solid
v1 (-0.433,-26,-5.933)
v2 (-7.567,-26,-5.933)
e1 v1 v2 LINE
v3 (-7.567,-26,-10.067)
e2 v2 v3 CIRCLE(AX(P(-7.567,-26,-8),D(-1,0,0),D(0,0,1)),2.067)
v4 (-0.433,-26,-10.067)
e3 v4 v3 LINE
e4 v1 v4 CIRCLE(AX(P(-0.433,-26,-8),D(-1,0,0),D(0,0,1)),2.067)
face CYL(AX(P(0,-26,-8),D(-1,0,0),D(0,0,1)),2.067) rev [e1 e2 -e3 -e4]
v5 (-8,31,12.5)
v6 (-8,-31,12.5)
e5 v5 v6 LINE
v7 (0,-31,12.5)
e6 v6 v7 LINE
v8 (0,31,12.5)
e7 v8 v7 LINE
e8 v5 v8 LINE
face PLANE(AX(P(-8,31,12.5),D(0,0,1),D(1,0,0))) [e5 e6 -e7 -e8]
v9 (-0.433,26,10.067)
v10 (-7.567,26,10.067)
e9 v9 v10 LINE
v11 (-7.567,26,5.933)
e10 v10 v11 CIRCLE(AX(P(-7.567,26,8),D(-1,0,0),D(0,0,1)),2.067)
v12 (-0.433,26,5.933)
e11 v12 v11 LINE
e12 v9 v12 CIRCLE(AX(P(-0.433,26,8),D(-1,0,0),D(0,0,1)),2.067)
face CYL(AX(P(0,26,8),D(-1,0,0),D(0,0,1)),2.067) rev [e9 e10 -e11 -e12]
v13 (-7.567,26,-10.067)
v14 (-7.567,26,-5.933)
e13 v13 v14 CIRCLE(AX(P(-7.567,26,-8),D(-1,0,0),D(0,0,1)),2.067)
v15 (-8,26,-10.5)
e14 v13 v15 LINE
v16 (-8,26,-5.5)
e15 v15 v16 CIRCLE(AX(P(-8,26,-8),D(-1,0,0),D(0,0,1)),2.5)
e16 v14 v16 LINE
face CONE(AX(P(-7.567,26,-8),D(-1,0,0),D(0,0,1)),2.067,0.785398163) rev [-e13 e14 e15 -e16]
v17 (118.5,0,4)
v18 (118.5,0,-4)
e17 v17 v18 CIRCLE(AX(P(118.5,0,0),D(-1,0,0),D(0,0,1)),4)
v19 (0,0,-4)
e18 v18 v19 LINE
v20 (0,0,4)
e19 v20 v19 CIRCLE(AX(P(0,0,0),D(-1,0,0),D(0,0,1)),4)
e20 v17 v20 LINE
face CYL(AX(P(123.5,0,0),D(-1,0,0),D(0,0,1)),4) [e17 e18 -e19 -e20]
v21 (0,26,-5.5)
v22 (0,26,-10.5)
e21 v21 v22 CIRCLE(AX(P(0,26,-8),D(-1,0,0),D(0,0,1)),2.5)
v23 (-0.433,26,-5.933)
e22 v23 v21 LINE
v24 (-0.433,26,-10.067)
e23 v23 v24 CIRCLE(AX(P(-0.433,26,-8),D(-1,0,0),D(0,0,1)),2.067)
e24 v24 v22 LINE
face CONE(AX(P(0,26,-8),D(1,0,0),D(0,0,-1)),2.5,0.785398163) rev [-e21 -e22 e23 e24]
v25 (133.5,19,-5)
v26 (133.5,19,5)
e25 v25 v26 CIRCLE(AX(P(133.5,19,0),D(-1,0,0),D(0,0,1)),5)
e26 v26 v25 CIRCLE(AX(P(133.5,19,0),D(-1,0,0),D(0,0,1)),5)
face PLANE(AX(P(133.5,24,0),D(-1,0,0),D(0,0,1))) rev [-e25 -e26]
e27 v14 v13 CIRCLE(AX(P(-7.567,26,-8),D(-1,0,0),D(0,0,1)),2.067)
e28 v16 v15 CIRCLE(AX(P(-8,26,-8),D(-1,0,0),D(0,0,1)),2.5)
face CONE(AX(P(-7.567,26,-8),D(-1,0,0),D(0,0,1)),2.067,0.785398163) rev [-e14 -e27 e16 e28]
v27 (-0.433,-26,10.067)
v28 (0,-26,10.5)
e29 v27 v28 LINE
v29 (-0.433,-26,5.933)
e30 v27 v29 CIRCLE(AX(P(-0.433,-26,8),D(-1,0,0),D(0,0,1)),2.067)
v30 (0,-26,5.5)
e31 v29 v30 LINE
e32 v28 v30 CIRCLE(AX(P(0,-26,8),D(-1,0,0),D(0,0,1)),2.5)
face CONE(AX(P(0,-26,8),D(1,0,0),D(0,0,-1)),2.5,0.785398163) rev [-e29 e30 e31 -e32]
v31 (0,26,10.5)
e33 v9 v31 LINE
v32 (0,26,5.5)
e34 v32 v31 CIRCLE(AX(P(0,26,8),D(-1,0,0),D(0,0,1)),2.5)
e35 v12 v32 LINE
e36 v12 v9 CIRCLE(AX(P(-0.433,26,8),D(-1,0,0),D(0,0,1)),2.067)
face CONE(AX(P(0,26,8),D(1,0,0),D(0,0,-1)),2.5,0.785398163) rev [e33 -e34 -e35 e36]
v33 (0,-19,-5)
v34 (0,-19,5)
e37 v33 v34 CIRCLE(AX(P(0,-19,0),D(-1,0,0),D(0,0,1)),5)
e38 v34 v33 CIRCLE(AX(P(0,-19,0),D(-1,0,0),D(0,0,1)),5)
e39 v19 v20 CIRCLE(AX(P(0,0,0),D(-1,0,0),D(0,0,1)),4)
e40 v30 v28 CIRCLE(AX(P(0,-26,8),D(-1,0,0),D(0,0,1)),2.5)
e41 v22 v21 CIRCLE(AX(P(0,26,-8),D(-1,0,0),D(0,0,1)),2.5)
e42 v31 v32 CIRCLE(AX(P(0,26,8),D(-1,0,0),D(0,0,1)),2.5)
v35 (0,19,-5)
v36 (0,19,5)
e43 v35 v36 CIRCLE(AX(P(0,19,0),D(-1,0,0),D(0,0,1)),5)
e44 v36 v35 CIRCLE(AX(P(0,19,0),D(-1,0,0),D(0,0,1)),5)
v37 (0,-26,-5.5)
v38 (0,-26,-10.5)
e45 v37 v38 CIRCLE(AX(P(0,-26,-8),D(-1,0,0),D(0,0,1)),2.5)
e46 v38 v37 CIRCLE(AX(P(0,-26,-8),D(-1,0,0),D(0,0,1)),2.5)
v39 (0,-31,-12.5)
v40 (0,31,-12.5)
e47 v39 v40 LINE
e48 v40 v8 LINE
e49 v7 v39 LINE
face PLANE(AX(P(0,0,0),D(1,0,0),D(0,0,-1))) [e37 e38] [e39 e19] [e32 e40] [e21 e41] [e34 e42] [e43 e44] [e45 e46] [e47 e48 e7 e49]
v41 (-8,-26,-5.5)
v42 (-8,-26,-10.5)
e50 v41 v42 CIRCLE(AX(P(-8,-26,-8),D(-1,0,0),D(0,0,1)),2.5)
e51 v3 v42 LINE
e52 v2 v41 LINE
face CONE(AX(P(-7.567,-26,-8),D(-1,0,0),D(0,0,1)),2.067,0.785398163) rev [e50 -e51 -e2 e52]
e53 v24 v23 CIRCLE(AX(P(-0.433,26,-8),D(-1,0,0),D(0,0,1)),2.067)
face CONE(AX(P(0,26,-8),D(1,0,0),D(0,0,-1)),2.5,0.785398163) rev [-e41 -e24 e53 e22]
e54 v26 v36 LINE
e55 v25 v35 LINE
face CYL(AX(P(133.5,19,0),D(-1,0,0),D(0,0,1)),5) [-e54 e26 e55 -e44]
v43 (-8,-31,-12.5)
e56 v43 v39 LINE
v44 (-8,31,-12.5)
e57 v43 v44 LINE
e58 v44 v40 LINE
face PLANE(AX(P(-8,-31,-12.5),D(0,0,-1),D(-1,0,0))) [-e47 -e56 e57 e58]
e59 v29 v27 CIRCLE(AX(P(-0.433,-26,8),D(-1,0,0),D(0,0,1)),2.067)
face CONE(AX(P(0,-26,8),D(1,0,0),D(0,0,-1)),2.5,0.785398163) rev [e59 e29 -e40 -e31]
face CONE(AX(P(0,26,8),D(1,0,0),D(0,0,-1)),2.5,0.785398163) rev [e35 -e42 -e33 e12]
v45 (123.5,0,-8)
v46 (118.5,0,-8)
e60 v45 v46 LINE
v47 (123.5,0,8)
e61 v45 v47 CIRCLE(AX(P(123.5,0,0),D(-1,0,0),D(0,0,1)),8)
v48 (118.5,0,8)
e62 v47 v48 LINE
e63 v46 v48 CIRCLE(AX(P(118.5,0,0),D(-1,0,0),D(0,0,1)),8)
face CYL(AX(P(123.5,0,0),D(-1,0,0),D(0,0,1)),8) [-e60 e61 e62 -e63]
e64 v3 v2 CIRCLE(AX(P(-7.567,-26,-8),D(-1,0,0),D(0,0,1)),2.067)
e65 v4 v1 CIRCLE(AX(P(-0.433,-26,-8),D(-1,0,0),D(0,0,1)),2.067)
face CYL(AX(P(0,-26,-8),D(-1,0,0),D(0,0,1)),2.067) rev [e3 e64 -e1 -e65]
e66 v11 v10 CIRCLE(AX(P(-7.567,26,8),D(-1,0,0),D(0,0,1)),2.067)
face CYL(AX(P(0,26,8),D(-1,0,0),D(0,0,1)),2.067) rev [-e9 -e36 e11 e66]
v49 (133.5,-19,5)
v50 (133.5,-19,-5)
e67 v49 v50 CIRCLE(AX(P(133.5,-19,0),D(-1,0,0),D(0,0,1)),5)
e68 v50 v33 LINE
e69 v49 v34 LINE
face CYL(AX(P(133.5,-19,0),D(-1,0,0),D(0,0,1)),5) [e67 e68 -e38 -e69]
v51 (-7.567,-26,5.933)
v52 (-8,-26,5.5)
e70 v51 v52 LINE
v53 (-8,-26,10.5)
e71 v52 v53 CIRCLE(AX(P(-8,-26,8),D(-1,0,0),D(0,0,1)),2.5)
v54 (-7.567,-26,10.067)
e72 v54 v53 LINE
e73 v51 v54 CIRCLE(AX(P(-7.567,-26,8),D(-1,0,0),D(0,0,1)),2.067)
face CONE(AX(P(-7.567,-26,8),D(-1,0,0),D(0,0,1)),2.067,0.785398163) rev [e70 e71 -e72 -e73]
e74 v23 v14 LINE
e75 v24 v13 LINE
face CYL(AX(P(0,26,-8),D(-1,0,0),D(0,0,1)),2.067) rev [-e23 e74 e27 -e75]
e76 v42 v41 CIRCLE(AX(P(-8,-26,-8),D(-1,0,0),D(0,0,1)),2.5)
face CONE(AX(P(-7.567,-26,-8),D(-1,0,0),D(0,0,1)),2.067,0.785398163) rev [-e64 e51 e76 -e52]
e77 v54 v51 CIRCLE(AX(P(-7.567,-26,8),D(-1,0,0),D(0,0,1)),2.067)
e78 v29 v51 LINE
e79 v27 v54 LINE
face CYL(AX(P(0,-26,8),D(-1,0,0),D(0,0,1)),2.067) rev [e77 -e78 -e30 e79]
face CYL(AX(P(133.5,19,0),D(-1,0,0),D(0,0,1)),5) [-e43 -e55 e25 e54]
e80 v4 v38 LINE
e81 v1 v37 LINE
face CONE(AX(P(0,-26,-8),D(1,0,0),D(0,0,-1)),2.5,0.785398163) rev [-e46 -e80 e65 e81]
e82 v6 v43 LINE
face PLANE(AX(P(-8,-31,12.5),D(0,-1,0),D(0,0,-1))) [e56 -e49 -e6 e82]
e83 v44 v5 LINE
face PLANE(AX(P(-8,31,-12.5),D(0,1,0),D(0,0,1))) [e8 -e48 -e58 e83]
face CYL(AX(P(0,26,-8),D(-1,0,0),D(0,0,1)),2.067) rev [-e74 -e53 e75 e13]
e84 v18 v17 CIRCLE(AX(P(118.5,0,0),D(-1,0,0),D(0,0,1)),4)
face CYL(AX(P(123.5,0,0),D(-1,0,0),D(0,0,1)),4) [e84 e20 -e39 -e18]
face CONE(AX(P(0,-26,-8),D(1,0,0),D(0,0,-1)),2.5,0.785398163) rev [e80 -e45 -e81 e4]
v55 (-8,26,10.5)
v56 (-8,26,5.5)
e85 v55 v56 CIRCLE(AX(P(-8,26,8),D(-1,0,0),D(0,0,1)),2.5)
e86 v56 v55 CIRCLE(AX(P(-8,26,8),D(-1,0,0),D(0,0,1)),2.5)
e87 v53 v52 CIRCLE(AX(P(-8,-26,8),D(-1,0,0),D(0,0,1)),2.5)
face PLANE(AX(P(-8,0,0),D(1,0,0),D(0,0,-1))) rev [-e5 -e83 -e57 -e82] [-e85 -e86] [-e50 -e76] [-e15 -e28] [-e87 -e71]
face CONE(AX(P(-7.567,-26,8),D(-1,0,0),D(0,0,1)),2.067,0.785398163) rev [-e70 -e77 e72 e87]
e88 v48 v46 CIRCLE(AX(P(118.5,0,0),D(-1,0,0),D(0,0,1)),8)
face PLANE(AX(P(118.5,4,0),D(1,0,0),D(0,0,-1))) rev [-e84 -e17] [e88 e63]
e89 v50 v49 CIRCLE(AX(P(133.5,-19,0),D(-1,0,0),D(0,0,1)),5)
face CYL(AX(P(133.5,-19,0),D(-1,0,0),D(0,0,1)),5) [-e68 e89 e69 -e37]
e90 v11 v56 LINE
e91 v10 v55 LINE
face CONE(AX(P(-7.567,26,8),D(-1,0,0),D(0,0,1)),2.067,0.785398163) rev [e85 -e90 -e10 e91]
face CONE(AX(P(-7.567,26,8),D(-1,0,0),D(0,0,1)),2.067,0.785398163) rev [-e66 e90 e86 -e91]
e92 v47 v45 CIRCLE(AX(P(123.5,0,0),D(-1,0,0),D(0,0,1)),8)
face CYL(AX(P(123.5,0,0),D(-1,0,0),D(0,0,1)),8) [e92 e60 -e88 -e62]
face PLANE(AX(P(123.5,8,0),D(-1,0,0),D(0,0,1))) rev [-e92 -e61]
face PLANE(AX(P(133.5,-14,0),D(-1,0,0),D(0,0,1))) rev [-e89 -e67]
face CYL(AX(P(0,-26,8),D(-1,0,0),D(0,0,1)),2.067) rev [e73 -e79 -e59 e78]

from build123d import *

# Parameters (mm, degrees)
SKETCH_1_W                  = 25
SKETCH_1_H                  = 62
EXTRUDE_1_DEPTH             = 8
SKETCH_2_W                  = 133.5
SKETCH_2_H                  = 5
PATTERN_LINEAR_1_COUNT      = 2
PATTERN_LINEAR_1_PITCH      = 38
PATTERN_LINEAR_2_COUNT      = 2
PATTERN_LINEAR_2_PITCH      = 16
PATTERN_LINEAR_2_COUNT_DIR2 = 2
PATTERN_LINEAR_2_PITCH_DIR2 = 52


with BuildPart() as part:
    # 草图1 → 凸台-拉伸1 (new body)
    with BuildSketch(Plane(origin=(0, 0, 0), x_dir=(0, 0, -1), z_dir=(1, 0, 0))):
        Rectangle(SKETCH_1_W, SKETCH_1_H)
    extrude(amount=-EXTRUDE_1_DEPTH)

    # 草图2 → 旋转1 (revolve)
    with BuildSketch(Plane.XY, mode=Mode.PRIVATE) as revolve_1_sk:
        with Locations((66.75, 21.5)):
            Rectangle(SKETCH_2_W, SKETCH_2_H)
    revolve_1 = revolve(revolve_1_sk.sketch.rotate(Axis((133.5, 19, 0), (-1, 0, 0)), 270), axis=Axis((133.5, 19, 0), (-1, 0, 0)))

    # 阵列(线性)1: 旋转1 ×2
    with Locations(*[(0, -i * PATTERN_LINEAR_1_PITCH, 0) for i in range(1, PATTERN_LINEAR_1_COUNT)]):
        add(revolve_1)

    # 草图4 → 切除-旋转1 (revolve, cut)
    with BuildSketch(Plane.XY.offset(8), mode=Mode.PRIVATE) as cut_revolve_1_sk:
        Polygon((-8, 26), (-8, 28.5), (-7.567, 28.067), (-0.433, 28.067), (0, 28.5), (0, 26), align=None)
    cut_revolve_1 = revolve(cut_revolve_1_sk.sketch.rotate(Axis((0, 26, 8), (-1, 0, 0)), 270), axis=Axis((0, 26, 8), (-1, 0, 0)), mode=Mode.SUBTRACT)

    # 阵列(线性)2: Cut-Revolve 1 2 × 2
    with Locations(*[(0, -j * PATTERN_LINEAR_2_PITCH_DIR2, -i * PATTERN_LINEAR_2_PITCH) for i in range(PATTERN_LINEAR_2_COUNT) for j in range(PATTERN_LINEAR_2_COUNT_DIR2) if (i, j) != (0, 0)]):
        add(cut_revolve_1, mode=Mode.SUBTRACT)

    # 草图6 → 旋转2 (revolve)
    with BuildSketch(Plane.XY, mode=Mode.PRIVATE) as revolve_2_sk:
        Polygon((0, 0), (0, 4), (118.5, 4), (118.5, 8), (123.5, 8), (123.5, 0), align=None)
    revolve(revolve_2_sk.sketch.rotate(Axis((123.5, 0, 0), (-1, 0, 0)), 270), axis=Axis((123.5, 0, 0), (-1, 0, 0)))


solid = part.part
